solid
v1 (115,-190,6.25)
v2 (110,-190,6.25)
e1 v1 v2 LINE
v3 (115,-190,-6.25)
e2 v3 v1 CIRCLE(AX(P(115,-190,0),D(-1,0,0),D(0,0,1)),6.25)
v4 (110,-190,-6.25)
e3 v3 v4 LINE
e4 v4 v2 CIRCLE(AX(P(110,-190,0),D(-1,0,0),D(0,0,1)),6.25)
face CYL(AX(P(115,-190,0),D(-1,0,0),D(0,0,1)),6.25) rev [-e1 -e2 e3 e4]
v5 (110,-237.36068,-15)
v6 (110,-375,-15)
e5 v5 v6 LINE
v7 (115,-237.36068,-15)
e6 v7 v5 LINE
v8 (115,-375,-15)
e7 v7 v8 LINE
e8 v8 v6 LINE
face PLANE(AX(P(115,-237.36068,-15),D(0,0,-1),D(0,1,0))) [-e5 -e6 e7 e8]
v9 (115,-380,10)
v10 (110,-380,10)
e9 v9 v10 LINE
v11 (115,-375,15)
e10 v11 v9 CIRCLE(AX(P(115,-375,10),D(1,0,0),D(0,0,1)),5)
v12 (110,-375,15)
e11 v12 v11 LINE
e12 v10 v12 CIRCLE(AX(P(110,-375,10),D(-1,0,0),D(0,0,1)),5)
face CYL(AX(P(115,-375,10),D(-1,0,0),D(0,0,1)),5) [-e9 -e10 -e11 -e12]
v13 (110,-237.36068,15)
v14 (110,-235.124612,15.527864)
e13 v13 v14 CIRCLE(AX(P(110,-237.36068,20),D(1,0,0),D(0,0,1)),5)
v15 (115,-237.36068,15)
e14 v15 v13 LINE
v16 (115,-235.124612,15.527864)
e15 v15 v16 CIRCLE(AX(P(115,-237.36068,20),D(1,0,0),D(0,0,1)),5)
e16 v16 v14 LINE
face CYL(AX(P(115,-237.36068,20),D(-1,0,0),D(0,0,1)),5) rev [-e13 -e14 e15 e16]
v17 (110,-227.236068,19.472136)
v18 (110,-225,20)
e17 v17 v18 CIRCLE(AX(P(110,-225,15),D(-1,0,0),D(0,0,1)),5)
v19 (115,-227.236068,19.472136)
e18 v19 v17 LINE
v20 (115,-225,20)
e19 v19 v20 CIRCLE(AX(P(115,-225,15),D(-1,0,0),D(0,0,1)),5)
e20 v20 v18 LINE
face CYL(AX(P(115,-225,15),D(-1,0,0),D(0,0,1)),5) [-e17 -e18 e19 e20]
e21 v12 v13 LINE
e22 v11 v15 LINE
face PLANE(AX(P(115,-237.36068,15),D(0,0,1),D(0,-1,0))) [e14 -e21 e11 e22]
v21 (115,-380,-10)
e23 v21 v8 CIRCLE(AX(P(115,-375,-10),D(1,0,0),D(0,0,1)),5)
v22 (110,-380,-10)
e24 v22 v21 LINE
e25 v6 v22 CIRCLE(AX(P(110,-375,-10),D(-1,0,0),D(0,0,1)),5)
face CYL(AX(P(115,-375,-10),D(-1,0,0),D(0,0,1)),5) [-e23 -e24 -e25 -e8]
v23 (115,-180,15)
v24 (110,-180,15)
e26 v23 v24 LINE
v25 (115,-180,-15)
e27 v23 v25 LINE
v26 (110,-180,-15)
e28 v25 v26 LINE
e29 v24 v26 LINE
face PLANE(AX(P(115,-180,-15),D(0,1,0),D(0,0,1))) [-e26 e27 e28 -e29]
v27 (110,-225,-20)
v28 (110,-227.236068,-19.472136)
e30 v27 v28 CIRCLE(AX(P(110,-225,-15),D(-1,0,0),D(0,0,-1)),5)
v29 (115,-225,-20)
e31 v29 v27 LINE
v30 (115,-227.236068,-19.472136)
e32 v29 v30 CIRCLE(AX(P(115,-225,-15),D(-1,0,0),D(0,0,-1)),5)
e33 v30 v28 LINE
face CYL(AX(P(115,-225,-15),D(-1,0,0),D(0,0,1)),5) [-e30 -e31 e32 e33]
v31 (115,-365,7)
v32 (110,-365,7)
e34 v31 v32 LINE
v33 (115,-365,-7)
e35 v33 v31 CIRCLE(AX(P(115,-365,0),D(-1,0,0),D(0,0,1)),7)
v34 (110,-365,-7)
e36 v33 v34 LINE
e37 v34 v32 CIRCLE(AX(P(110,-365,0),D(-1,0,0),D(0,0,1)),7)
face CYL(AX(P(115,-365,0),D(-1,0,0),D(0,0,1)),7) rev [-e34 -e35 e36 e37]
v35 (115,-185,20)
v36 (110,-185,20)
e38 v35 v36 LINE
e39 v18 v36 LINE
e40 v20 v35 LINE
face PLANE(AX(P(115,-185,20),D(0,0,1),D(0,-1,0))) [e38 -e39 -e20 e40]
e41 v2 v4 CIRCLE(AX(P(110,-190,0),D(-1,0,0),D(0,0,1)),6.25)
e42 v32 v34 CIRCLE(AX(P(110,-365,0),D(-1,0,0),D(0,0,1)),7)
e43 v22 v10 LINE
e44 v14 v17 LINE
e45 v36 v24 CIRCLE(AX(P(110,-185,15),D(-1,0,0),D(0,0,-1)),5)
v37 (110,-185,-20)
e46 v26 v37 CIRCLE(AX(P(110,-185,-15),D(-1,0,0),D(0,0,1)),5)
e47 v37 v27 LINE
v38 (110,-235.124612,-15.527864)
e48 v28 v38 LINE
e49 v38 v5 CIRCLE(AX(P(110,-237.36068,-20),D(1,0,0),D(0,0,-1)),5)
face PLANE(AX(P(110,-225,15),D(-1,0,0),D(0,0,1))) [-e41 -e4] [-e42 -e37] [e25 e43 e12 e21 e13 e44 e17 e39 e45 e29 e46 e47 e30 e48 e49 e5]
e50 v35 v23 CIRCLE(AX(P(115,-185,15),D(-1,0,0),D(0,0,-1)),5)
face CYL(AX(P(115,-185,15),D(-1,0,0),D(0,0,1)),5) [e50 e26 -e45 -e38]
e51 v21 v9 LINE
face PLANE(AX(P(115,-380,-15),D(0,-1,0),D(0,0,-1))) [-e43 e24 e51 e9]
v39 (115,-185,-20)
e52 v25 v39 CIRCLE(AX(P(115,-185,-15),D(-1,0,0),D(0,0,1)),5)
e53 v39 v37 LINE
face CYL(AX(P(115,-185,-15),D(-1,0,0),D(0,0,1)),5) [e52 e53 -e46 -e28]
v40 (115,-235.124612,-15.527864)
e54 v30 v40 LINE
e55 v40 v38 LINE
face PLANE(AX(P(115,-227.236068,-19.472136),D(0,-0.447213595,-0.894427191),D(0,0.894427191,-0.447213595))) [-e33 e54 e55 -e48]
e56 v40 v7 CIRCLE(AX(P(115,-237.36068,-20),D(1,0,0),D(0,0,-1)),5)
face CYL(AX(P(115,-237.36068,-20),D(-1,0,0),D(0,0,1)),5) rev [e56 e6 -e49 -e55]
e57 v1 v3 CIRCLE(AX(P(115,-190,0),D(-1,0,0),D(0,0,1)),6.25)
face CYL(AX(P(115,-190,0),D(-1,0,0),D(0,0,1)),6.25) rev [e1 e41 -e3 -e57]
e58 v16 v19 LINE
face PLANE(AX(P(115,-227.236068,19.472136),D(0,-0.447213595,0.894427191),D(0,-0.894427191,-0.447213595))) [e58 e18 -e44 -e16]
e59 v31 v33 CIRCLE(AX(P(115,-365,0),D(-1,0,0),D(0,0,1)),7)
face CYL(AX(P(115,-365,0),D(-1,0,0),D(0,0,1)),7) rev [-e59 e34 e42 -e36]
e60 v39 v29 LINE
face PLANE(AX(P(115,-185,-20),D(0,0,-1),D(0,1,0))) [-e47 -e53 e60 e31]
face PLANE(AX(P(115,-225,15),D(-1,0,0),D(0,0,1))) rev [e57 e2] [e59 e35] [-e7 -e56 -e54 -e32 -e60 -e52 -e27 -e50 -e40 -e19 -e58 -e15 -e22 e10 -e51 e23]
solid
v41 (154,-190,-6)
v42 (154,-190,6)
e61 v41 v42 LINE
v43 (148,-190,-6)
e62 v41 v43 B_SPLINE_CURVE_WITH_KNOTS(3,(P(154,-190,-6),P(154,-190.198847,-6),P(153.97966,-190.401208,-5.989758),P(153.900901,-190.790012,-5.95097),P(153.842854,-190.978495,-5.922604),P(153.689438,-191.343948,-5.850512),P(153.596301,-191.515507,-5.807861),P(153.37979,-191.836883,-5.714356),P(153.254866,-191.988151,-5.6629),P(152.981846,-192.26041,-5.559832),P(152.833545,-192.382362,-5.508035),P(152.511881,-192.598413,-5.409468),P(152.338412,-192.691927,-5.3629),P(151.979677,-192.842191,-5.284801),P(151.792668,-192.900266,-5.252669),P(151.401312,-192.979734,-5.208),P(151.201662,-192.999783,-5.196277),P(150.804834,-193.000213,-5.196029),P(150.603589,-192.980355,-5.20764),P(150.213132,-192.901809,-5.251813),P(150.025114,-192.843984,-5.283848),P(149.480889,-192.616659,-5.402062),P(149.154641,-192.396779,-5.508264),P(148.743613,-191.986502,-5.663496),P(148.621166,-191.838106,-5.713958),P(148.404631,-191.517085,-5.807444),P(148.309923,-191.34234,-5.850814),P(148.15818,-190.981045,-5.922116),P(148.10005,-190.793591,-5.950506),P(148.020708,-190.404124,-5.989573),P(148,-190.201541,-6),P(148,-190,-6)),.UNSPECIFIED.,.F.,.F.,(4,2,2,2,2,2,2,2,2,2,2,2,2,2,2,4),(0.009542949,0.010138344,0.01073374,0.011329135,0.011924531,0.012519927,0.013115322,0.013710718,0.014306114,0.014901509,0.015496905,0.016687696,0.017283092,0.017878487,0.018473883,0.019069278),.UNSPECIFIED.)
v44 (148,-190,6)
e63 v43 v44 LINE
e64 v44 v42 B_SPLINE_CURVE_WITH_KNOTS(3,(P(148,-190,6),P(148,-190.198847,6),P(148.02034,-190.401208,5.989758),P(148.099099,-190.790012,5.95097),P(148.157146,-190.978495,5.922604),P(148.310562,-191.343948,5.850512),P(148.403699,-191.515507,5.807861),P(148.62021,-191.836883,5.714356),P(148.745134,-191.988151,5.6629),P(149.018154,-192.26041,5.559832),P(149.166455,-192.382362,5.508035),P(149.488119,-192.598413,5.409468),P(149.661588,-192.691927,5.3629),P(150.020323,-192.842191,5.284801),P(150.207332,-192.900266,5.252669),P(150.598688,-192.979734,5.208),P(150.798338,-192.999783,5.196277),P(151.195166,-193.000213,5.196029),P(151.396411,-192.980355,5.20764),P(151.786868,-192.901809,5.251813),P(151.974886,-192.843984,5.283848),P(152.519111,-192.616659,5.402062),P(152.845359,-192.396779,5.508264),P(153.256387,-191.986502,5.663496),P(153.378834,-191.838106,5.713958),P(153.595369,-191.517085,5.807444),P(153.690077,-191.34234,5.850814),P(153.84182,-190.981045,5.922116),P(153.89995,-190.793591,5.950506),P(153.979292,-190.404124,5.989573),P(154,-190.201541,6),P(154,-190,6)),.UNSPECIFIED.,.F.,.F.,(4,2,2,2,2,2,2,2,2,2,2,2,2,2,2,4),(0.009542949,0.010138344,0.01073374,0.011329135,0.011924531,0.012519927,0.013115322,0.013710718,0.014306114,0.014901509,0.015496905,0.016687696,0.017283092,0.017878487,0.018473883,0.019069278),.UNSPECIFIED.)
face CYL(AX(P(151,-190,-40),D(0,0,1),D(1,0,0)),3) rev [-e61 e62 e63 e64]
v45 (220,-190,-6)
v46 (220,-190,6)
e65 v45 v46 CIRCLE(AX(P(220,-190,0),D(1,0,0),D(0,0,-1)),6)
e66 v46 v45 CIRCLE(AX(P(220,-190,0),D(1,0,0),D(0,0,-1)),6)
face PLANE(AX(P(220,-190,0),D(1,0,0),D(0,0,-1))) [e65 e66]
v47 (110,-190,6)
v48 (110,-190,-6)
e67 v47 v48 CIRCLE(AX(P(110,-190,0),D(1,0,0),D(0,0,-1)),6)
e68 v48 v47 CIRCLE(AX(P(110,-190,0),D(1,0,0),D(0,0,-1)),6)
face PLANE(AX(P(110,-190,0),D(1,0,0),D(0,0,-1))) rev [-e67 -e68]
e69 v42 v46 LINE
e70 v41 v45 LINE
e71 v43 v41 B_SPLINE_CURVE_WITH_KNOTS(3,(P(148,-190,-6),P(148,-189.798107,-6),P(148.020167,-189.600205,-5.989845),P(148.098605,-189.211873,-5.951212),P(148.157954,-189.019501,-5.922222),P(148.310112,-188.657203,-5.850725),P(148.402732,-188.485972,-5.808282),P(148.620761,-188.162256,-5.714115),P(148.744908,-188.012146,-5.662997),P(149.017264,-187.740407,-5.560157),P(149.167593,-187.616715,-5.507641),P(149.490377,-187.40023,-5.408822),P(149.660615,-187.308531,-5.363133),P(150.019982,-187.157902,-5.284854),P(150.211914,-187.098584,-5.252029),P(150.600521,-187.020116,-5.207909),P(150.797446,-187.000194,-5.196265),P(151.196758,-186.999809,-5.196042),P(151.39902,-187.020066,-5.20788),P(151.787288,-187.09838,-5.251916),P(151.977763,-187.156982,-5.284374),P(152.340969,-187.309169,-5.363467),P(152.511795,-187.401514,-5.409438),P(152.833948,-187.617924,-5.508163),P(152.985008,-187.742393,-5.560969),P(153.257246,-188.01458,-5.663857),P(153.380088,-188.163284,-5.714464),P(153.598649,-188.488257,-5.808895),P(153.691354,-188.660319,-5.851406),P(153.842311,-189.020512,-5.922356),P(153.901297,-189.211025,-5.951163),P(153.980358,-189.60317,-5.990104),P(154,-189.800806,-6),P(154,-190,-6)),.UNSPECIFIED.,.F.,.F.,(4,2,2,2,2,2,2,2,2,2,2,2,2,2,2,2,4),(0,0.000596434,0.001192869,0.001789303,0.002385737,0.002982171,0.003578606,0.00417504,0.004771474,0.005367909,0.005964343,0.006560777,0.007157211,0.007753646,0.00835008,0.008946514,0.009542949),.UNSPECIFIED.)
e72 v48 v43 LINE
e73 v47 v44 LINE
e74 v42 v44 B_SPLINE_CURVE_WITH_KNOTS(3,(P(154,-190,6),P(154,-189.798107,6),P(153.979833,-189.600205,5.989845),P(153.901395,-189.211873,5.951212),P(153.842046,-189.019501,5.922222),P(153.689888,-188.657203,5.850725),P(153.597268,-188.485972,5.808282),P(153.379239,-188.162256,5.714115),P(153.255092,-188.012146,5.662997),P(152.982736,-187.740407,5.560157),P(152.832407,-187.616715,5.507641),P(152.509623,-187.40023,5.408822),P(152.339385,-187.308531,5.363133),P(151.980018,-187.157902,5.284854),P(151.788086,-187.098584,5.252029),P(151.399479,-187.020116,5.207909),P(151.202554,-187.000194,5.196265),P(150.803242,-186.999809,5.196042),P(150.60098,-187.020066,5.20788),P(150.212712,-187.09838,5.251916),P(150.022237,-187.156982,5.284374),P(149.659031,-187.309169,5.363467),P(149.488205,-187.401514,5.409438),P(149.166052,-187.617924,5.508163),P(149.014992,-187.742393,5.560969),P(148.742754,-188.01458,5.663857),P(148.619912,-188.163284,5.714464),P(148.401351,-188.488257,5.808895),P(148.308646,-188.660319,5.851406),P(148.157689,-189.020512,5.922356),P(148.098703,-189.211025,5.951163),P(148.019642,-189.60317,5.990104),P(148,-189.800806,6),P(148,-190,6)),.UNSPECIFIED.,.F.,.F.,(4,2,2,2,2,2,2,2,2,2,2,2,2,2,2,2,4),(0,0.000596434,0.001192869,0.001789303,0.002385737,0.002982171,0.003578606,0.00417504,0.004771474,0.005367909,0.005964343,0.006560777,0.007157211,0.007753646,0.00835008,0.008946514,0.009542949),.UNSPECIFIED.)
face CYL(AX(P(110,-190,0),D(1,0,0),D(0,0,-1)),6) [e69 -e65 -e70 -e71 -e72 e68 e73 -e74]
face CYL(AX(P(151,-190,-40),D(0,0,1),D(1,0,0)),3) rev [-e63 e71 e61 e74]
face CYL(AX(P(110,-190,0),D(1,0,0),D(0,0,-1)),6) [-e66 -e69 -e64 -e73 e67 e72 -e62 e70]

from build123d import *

# Parameters (mm, degrees)
SWEEP_1_PROFILE_R   = 6
SKETCH_4_R          = 3
CUT_EXTRUDE_2_DEPTH = 40
SKETCH_6_R          = 7
SKETCH_6_R_2        = 6.25
EXTRUDE_2_DEPTH     = 5
FILLET_1_R          = 5


with BuildPart() as part:
    # 扫描1: sweep along a path in 草图1
    with BuildLine(Plane.XY) as sweep_1_path:
        Line((110, -190), (220, -190))
    # 扫描1 profile (on start of the path) → 扫描1 (sweep)
    with BuildSketch(Plane(origin=(110, -190, 0), x_dir=(0, 0, 1), z_dir=(1, 0, 0))):
        Circle(SWEEP_1_PROFILE_R)
    sweep(path=sweep_1_path.line)

    # 草图4 → 切除-拉伸2 (cut, symmetric)
    with BuildSketch(Plane.XY):
        with Locations((151, -190)):
            Circle(SKETCH_4_R)
    extrude(amount=CUT_EXTRUDE_2_DEPTH, both=True, mode=Mode.SUBTRACT)


with BuildPart() as body_2:
    # 草图6 → 凸台-拉伸2 (new body)
    with BuildSketch(Plane.ZY.offset(-110)):
        with BuildLine():
            Line((-19.472135955, -227.236067977), (-15.527864045, -235.124611797))
            ThreePointArc((-15.527864045, -235.124611797), (-15.133755053, -236.211915172), (-15, -237.360679775))
            Line((-15, -237.360679775), (-15, -380))
            Line((-15, -380), (15, -380))
            Line((15, -380), (15, -237.360679775))
            ThreePointArc((15, -237.360679775), (15.133755053, -236.211915172), (15.527864045, -235.124611797))
            Line((15.527864045, -235.124611797), (19.472135955, -227.236067977))
            ThreePointArc((19.472135955, -227.236067977), (19.866244947, -226.148764603), (20, -225))
            Line((20, -225), (20, -185))
            ThreePointArc((20, -185), (18.535533906, -181.464466094), (15, -180))
            Line((15, -180), (-15, -180))
            ThreePointArc((-15, -180), (-18.535533906, -181.464466094), (-20, -185))
            Line((-20, -185), (-20, -225))
            ThreePointArc((-20, -225), (-19.866244947, -226.148764603), (-19.472135955, -227.236067977))
        make_face()
        with Locations((0, -365)):
            Circle(SKETCH_6_R, mode=Mode.SUBTRACT)
        with Locations((0, -190)):
            Circle(SKETCH_6_R_2, mode=Mode.SUBTRACT)
    extrude(amount=-EXTRUDE_2_DEPTH)

    # 圆角1
    fillet_1_edges = [body_2.edges().sort_by_distance(p)[0] for p in [
        (112.5, -380, 15),
        (112.5, -380, -15),
    ]]
    fillet(fillet_1_edges, radius=FILLET_1_R)


solid = Compound([part.part, body_2.part])
